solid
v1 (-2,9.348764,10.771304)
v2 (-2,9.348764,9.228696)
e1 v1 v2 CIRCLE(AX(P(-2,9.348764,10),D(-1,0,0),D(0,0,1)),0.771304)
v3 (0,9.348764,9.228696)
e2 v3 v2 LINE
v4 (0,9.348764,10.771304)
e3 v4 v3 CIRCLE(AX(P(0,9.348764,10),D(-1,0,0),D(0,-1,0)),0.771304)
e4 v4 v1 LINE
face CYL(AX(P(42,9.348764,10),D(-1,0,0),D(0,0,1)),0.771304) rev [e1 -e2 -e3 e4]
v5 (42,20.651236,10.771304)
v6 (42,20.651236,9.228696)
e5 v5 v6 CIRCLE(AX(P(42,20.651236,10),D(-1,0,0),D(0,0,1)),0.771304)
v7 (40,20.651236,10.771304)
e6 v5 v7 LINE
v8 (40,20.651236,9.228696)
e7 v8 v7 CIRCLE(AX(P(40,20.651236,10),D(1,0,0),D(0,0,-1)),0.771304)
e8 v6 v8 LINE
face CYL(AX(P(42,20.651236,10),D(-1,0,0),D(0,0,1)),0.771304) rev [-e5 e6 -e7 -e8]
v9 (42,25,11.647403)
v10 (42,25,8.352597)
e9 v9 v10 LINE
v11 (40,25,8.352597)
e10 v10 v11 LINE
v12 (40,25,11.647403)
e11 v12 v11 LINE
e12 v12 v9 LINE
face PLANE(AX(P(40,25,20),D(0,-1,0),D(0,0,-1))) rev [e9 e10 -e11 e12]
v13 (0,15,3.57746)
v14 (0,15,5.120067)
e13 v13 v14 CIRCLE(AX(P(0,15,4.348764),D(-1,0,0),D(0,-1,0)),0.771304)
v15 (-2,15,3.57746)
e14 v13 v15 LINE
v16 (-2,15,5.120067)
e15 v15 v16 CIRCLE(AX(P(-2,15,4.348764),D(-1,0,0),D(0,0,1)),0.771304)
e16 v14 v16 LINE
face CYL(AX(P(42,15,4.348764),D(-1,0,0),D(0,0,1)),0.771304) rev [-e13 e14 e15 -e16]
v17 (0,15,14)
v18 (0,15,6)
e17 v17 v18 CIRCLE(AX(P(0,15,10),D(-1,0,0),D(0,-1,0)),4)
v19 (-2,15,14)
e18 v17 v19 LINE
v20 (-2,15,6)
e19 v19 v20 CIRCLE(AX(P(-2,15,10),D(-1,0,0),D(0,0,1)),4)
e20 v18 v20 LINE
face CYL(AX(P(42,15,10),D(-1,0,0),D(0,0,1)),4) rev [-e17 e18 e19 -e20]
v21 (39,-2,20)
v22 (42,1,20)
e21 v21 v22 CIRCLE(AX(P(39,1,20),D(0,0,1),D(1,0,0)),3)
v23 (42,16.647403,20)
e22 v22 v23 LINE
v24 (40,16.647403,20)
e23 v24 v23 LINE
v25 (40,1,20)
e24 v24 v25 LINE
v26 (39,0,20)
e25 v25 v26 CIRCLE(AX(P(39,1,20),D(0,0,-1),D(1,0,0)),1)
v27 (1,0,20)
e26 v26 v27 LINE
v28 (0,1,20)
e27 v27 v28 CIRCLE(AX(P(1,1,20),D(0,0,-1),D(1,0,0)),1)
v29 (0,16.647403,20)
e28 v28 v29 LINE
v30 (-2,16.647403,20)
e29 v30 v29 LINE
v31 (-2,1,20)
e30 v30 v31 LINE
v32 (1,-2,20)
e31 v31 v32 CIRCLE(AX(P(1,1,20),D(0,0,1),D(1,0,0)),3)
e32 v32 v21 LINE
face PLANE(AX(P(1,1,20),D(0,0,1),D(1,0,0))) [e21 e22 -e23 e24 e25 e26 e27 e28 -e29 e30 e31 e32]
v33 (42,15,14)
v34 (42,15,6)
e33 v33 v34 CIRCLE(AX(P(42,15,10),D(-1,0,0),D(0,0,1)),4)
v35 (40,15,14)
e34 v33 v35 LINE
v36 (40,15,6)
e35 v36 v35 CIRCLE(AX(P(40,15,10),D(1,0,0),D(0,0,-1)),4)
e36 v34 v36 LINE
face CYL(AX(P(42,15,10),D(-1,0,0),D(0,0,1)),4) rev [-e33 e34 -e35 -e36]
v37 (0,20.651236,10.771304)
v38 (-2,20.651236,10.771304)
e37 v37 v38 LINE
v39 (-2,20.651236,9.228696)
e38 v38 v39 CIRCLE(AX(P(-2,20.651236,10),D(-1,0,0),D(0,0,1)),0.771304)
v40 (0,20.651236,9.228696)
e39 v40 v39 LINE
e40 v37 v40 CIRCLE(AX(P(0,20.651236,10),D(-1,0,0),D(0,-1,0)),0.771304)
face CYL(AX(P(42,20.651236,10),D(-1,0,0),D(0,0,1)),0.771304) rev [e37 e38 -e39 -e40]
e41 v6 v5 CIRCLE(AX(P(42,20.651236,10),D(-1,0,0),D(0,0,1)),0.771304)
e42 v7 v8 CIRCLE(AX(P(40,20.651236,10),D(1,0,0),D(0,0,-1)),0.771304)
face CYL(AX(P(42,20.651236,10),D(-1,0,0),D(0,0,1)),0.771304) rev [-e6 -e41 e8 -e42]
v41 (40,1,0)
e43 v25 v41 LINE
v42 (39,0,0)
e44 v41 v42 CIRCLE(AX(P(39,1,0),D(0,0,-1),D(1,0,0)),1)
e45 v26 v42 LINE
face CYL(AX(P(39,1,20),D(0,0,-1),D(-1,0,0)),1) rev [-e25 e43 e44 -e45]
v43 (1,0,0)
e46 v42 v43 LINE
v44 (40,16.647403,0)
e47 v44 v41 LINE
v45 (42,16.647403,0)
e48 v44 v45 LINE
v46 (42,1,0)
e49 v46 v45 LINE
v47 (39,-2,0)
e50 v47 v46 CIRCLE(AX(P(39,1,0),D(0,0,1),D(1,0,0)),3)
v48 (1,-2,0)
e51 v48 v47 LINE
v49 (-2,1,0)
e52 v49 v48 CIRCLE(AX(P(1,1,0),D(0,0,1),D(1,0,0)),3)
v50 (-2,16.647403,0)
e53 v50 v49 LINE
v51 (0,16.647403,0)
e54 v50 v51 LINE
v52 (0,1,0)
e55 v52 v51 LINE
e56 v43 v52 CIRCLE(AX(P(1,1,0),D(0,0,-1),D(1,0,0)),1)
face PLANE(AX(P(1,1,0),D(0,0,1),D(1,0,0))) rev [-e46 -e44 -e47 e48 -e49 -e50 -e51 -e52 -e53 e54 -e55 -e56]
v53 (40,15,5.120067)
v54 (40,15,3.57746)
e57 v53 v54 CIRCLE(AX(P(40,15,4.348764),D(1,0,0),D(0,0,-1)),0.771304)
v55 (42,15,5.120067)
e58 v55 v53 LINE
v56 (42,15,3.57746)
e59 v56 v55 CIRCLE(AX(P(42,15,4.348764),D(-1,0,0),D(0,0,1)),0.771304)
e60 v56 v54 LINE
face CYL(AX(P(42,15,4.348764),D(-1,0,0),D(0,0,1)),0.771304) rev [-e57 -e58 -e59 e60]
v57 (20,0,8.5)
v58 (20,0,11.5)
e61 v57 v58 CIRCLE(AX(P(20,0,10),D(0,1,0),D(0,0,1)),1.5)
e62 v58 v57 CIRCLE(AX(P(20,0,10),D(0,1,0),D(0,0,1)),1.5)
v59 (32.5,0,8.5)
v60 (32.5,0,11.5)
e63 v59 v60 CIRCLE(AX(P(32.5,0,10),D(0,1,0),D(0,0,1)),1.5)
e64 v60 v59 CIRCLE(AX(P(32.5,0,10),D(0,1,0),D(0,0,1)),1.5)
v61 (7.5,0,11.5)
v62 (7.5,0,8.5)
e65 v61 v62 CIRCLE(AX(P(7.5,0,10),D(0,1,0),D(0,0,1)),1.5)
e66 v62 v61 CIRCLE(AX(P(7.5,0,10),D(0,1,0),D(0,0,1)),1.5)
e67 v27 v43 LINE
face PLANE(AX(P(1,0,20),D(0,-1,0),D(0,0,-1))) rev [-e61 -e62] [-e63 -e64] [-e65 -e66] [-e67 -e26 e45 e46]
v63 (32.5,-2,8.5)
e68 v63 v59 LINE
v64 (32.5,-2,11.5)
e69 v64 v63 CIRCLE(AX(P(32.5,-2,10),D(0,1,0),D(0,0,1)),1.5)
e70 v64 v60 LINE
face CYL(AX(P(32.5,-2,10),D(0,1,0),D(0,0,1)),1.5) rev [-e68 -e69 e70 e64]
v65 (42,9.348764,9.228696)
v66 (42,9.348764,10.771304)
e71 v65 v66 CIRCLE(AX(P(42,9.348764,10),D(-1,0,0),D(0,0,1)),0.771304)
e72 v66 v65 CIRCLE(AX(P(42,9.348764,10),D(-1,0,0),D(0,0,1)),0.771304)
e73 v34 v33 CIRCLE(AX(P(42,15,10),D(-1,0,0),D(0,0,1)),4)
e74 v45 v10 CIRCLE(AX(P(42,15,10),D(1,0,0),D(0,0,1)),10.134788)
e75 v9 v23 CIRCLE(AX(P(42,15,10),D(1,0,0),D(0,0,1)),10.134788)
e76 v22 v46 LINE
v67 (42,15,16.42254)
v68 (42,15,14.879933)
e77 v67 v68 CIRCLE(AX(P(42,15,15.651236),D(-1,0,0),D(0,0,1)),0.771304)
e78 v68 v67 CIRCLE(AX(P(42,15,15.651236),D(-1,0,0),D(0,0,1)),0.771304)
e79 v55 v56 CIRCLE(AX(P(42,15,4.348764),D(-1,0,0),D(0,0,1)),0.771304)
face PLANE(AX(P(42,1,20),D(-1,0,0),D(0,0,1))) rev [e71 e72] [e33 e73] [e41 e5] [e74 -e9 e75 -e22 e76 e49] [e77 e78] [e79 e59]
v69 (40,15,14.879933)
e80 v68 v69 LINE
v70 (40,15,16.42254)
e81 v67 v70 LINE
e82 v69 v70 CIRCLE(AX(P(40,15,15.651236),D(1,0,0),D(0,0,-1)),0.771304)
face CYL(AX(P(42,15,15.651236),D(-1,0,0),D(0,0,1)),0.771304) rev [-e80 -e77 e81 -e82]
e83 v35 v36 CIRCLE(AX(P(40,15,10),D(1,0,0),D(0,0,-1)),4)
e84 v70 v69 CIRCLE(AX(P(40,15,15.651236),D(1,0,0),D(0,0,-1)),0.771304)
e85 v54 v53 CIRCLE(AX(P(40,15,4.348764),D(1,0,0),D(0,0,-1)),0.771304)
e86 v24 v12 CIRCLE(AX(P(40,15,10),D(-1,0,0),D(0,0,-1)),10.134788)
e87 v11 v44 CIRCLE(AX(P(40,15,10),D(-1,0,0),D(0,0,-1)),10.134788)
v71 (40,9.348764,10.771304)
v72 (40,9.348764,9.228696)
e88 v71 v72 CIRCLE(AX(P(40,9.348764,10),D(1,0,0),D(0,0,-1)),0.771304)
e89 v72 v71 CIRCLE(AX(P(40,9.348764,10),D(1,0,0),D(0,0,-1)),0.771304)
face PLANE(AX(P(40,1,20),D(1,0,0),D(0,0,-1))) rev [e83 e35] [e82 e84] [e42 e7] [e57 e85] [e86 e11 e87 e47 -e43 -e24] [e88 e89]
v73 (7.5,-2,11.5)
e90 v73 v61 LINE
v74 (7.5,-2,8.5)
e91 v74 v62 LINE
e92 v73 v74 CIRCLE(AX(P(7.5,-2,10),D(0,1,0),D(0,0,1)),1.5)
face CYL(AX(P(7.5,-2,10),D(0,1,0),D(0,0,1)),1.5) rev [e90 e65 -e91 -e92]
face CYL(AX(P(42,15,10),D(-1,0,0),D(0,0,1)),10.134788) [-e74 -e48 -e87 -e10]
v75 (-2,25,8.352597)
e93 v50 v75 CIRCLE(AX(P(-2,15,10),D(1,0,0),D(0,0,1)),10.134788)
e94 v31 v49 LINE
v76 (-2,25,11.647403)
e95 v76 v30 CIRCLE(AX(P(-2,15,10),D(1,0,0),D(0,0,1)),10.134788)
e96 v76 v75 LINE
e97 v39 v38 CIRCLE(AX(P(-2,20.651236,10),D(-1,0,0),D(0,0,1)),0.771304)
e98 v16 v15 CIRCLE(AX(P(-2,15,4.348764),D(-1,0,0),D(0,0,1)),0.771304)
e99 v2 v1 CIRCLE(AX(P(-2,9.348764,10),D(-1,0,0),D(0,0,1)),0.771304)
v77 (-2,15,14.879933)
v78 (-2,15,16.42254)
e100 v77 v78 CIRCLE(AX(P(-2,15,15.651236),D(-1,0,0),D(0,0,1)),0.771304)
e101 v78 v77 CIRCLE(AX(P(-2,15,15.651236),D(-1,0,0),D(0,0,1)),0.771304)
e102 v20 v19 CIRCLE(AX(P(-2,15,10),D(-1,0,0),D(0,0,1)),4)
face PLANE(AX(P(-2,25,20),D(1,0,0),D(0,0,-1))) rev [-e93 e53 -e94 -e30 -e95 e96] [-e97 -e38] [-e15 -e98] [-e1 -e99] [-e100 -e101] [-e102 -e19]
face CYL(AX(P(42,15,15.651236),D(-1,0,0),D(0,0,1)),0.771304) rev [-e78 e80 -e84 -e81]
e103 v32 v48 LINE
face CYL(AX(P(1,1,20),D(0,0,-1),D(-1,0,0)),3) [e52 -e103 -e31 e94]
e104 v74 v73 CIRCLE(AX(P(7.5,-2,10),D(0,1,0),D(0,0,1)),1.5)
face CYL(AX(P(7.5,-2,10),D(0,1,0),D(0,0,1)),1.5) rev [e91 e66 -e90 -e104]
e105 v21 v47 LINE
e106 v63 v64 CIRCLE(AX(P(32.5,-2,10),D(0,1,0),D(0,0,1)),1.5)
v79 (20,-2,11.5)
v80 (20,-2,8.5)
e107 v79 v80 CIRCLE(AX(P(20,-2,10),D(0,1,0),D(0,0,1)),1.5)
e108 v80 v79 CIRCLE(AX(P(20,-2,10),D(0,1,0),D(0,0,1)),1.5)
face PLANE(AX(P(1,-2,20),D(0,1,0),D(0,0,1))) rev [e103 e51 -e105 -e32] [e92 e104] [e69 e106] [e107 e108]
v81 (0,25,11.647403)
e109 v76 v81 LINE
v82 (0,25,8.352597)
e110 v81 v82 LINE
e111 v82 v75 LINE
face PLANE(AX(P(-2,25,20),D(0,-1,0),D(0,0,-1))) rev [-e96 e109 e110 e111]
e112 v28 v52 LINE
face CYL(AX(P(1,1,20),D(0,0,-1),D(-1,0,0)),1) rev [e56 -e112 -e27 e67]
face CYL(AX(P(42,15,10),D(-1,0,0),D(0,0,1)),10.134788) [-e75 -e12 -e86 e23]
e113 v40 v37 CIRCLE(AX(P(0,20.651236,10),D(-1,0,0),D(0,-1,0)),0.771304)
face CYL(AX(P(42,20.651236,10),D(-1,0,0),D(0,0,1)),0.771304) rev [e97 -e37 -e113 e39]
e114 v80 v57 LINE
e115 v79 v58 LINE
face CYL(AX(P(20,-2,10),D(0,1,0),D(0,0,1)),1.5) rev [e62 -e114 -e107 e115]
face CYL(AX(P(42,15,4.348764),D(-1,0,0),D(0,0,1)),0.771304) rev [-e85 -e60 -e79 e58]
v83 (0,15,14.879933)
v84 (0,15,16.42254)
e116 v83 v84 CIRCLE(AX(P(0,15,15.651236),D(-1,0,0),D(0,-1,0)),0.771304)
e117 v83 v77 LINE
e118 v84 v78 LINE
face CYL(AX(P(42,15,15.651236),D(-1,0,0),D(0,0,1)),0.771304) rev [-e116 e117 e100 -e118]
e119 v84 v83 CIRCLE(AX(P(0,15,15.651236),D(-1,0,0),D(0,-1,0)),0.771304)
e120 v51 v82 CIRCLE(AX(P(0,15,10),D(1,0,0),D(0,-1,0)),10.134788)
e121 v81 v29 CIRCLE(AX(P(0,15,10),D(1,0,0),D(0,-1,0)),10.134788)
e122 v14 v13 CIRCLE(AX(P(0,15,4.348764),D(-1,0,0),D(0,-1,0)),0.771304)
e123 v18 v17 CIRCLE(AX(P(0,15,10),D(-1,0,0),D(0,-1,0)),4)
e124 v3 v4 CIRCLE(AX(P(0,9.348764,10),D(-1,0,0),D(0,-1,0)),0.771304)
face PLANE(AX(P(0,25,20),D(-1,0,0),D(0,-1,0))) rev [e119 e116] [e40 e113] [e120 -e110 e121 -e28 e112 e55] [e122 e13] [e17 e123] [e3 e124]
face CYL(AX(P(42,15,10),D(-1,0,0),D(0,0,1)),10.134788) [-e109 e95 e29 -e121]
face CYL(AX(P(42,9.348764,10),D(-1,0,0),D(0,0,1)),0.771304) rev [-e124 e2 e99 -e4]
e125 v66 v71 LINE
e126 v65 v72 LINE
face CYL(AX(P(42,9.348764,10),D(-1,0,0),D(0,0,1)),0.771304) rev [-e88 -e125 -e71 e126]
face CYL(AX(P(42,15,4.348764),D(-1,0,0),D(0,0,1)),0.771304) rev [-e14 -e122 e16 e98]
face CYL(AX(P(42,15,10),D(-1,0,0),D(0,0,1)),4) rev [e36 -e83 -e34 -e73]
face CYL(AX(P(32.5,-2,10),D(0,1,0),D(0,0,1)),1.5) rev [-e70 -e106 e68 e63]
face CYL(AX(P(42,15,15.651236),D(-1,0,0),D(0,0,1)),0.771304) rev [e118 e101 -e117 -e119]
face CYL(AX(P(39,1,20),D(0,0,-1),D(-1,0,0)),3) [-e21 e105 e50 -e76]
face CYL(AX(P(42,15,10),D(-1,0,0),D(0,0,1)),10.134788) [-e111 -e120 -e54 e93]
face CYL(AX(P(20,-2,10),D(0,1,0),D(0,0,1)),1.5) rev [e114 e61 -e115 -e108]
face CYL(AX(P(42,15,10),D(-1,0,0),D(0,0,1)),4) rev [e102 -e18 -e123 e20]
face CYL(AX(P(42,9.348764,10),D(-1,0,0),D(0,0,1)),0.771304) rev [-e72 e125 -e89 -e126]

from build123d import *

# Parameters (mm, degrees)
BOSS_EXTRUDE1_DEPTH = 20
SKETCH2_R           = 4
SKETCH2_R_2         = 0.771303816
CUT_EXTRUDE1_DEPTH  = 55.415071442
SKETCH3_R           = 1.5
CUT_EXTRUDE2_DEPTH  = 53.810983706


with BuildPart() as part:
    # Sketch1 → Boss-Extrude1 (new body)
    with BuildSketch(Plane.XY):
        with BuildLine():
            Line((0, 25), (0, 1))
            ThreePointArc((0, 1), (0.292893219, 0.292893219), (1, 0))
            Line((1, 0), (39, 0))
            ThreePointArc((39, 0), (39.707106781, 0.292893219), (40, 1))
            Line((40, 1), (40, 25))
            Line((40, 25), (42, 25))
            Line((42, 25), (42, 1))
            ThreePointArc((42, 1), (41.121320344, -1.121320344), (39, -2))
            Line((39, -2), (1, -2))
            ThreePointArc((1, -2), (-1.121320344, -1.121320344), (-2, 1))
            Line((-2, 1), (-2, 25))
            Line((-2, 25), (0, 25))
        make_face()
    extrude(amount=BOSS_EXTRUDE1_DEPTH)

    # Sketch2 → Cut-Extrude1 (cut, through all)
    with BuildSketch(Plane.ZY.offset(2)):
        with Locations((10, 15)):
            Circle(SKETCH2_R)
        with Locations((10, 20.651236345)):
            Circle(SKETCH2_R_2)
        with Locations((15.651236345, 15)):
            Circle(SKETCH2_R_2)
        with Locations((10, 9.348763655)):
            Circle(SKETCH2_R_2)
        with Locations((4.348763655, 15)):
            Circle(SKETCH2_R_2)
        with BuildLine():
            Line((-0.134788382, 15), (-9.479992385, 25.134788382))
            Line((-9.479992385, 25.134788382), (9.199881334, 33.71105644))
            Line((9.199881334, 33.71105644), (31.219173818, 26.927862072))
            Line((31.219173818, 26.927862072), (20.134788382, 15))
            ThreePointArc((20.134788382, 15), (10, 25.134788382), (-0.134788382, 15))
        make_face()
    extrude(amount=-CUT_EXTRUDE1_DEPTH, mode=Mode.SUBTRACT)

    # Sketch3 → Cut-Extrude2 (cut, through all)
    with BuildSketch(Plane(origin=(0, 0, 0), x_dir=(1, 0, 0), z_dir=(0, 1, 0))):
        with Locations(Location((7.5, -10, 0), (0, 0, 270))):
            Circle(SKETCH3_R)
        with Locations(Location((20, -10, 0), (0, 0, 270))):
            Circle(SKETCH3_R)
        with Locations(Location((32.5, -10, 0), (0, 0, 270))):
            Circle(SKETCH3_R)
    extrude(amount=-CUT_EXTRUDE2_DEPTH, mode=Mode.SUBTRACT)


solid = part.part
